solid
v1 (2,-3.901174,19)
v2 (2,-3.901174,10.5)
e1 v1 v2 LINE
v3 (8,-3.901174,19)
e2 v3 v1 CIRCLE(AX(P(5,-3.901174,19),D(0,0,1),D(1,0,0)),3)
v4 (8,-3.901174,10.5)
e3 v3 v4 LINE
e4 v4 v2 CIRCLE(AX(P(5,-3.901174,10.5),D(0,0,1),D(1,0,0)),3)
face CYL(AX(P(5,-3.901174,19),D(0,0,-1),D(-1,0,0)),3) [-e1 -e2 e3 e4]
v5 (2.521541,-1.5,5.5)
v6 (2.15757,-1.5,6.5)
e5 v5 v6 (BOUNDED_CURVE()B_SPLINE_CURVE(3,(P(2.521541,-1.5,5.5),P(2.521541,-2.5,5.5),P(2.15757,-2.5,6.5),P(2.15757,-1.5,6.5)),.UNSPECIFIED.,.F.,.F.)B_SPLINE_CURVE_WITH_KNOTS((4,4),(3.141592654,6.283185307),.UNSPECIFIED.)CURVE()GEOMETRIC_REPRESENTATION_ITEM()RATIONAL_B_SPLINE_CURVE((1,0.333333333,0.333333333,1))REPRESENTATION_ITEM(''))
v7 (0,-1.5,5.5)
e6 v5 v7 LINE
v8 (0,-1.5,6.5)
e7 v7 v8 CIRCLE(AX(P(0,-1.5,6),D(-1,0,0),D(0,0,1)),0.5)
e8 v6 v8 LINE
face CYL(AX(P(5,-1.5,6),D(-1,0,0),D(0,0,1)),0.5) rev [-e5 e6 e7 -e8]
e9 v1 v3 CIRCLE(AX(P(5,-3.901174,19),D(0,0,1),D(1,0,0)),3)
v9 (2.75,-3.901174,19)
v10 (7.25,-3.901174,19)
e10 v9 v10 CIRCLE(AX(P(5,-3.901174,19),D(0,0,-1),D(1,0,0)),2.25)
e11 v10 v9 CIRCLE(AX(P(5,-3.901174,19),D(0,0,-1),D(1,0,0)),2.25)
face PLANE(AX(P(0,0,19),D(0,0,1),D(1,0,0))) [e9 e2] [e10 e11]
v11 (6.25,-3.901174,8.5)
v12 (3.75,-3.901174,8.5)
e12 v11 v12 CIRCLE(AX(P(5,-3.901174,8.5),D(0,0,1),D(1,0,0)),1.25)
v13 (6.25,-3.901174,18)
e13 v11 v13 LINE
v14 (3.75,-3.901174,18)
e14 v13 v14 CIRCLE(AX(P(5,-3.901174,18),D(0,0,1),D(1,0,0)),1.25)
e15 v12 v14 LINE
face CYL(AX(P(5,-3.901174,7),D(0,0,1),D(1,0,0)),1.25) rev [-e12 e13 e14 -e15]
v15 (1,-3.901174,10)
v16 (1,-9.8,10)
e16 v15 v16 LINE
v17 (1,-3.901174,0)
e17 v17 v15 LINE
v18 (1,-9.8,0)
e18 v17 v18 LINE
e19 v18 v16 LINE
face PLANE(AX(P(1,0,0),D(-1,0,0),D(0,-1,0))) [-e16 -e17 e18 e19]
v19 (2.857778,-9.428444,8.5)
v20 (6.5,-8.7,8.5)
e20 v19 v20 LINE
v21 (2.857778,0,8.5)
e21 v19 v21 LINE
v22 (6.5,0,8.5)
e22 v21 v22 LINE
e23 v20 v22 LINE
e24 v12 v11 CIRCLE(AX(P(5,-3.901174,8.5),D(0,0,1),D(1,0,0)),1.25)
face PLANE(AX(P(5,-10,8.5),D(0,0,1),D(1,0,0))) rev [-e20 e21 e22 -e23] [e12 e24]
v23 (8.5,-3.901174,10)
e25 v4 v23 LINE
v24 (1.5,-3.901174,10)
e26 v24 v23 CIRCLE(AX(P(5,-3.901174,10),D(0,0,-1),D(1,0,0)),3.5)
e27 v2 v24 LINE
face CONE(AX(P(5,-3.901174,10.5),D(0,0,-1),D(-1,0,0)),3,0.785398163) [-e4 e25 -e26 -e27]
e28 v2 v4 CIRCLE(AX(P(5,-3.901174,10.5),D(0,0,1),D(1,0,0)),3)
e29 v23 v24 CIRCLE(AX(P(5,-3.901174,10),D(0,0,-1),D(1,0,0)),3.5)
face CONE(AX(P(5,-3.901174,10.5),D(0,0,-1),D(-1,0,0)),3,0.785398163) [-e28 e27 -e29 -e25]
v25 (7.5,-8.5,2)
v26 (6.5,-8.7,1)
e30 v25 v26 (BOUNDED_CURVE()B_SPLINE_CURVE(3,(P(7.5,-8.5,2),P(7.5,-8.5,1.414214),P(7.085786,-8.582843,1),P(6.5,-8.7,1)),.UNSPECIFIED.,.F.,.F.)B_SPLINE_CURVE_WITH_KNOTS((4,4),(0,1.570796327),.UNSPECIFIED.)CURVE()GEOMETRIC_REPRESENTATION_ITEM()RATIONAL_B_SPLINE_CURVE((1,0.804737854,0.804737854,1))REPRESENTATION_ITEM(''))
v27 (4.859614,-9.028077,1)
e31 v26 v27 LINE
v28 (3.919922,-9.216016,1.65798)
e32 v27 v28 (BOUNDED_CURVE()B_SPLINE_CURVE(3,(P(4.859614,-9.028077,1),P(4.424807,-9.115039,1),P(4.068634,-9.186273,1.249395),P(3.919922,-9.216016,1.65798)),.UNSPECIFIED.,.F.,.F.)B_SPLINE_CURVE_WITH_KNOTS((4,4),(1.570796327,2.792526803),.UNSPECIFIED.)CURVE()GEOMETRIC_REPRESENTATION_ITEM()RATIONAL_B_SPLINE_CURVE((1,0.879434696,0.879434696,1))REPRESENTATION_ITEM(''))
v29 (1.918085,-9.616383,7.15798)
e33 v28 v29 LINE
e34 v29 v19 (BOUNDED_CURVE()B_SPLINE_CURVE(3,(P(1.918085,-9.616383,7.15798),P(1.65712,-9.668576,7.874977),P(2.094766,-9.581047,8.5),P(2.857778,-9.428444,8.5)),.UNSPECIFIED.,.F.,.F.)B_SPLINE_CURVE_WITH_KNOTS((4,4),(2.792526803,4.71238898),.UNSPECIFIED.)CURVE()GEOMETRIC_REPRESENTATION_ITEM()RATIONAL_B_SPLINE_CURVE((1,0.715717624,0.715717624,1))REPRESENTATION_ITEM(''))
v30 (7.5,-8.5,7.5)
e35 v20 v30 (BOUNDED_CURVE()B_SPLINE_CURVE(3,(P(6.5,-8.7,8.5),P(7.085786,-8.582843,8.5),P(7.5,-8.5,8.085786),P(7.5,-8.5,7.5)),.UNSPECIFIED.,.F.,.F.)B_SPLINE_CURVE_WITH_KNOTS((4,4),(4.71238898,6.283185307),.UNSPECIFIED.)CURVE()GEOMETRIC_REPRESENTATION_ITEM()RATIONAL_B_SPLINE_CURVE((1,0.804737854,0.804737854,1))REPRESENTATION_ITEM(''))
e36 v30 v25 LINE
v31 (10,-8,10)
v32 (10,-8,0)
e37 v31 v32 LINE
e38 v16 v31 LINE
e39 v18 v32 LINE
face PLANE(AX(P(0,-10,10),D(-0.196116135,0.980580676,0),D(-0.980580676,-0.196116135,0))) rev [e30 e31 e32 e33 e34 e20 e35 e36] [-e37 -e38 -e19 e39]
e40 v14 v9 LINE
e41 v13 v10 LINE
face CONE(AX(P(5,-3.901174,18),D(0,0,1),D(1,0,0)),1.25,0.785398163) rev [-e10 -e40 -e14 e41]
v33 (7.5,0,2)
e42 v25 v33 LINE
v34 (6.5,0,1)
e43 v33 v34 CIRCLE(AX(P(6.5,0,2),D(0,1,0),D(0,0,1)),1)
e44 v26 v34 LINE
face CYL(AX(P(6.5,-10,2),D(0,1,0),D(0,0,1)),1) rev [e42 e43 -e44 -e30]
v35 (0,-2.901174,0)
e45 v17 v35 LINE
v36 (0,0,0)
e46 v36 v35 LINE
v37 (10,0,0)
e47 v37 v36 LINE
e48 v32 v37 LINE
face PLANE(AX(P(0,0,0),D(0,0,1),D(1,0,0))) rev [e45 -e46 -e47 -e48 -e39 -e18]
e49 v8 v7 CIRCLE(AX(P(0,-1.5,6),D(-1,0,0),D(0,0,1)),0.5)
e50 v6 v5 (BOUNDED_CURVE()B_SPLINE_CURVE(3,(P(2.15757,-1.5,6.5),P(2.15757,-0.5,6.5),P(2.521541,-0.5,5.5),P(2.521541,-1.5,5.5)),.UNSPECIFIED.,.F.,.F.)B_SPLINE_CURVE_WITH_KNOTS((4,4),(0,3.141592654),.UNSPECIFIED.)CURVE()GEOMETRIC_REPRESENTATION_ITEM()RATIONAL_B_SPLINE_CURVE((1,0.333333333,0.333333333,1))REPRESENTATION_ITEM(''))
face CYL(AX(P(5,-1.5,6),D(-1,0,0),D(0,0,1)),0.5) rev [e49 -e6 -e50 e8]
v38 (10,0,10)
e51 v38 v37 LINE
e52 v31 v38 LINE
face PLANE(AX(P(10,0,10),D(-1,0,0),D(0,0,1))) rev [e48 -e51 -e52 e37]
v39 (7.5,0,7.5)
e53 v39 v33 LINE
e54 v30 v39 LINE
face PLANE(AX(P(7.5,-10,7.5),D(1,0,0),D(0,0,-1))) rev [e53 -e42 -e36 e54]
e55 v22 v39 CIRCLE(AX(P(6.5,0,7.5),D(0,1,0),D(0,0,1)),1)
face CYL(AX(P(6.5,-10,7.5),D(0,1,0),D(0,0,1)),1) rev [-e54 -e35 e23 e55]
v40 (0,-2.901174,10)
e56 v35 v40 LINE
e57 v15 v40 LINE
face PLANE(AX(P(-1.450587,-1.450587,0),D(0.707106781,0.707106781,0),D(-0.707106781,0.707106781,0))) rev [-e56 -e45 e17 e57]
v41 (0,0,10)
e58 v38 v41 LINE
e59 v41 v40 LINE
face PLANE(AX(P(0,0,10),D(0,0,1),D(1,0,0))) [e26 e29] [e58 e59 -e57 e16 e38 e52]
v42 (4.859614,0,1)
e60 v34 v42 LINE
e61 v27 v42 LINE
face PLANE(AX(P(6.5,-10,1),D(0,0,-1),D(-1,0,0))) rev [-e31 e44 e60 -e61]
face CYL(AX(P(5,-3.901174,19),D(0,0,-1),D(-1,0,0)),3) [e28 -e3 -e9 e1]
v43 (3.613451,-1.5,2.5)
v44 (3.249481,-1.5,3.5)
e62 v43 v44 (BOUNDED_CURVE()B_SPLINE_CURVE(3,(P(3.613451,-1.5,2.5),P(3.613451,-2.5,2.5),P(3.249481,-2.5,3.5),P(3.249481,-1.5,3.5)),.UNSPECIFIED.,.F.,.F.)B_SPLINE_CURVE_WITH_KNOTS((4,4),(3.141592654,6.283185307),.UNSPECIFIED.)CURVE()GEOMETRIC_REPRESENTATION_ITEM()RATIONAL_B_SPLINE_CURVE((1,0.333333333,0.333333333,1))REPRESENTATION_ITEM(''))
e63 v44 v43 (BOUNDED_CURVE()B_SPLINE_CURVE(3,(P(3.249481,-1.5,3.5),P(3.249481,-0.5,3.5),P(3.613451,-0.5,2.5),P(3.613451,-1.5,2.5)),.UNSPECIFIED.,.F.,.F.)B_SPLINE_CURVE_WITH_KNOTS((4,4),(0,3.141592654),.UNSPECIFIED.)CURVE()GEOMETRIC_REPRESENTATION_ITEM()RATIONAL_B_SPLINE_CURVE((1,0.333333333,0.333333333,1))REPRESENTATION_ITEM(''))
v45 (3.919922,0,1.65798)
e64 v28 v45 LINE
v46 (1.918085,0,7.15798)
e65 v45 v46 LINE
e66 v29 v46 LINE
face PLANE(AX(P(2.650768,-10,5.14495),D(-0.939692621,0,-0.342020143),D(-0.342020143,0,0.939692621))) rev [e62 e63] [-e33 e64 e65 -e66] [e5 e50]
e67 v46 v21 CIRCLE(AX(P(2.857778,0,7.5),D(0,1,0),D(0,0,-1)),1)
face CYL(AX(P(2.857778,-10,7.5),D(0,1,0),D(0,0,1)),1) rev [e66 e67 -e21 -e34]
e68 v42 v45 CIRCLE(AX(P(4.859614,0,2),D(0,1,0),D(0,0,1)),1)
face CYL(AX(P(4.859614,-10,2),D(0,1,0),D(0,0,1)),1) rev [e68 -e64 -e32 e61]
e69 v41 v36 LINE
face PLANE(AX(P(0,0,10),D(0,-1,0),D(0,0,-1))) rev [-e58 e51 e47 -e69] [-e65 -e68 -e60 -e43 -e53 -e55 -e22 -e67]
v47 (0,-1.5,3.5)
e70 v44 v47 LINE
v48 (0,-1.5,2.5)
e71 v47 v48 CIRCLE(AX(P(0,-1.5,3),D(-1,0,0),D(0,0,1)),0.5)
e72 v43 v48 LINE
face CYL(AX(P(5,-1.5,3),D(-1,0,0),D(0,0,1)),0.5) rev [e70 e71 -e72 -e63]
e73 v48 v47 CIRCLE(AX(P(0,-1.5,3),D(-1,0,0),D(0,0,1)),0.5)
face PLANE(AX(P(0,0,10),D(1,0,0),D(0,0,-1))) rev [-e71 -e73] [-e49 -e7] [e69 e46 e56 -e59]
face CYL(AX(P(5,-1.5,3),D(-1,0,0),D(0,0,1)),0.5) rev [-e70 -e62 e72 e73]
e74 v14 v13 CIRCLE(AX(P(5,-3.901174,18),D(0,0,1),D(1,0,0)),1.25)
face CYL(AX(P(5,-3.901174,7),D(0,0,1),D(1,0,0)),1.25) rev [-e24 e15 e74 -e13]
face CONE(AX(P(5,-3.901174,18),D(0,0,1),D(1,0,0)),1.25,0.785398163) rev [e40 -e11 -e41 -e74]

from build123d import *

# Parameters (mm, degrees)
BASE_BLOCK_DEPTH        = 10
ROUND_SPIGOT_DEPTH      = 9
PROFILE_CUT_A_DEPTH     = 10
TRIANGULAR_POCKET_DEPTH = 10
PROFILE_CUT_B_SKETCH_R  = 0.5
PROFILE_CUT_B_DEPTH     = 5
SPIGOT_CHAMFER_0_5_SIZE = 0.5
SPIGOT_BORE_SKETCH_R    = 1.25
SPIGOT_BORE_DEPTH       = 12
BORE_CHAMFER_1_SIZE     = 1


with BuildPart() as part:
    # Base Block Sketch → Base Block (new body)
    with BuildSketch(Plane.XY):
        Polygon((0, 0), (10, 0), (10, -8), (0, -10), align=None)
    extrude(amount=BASE_BLOCK_DEPTH)

    # Spigot Sketch → Round Spigot (add)
    with BuildSketch(Plane.XY.offset(10)):
        with BuildLine():
            ThreePointArc((5, -0.901174016), (2, -3.901174016), (5, -6.901174016))
            Line((5, -6.901174016), (5, -3.901174016))
            Line((5, -3.901174016), (5, -0.901174016))
        make_face()
        with BuildLine():
            Line((5, -3.901174016), (5, -6.901174016))
            ThreePointArc((5, -6.901174016), (5.282604808, -6.887833442), (5.562696209, -6.847930365))
            Line((5.562696209, -6.847930365), (5, -3.901174016))
        make_face()
        with BuildLine():
            Line((5, -3.901174016), (5.562696209, -6.847930365))
            ThreePointArc((5.562696209, -6.847930365), (7.311718909, -5.813229373), (8, -3.901174016))
            ThreePointArc((8, -3.901174016), (7.121320344, -1.779853673), (5, -0.901174016))
            Line((5, -0.901174016), (5, -3.901174016))
        make_face()
    extrude(amount=ROUND_SPIGOT_DEPTH)

    # Profile Cut A Sketch → Profile Cut A (cut)
    with BuildSketch(Plane.XY.offset(10)):
        Polygon((1, -9.8), (1, -3.901174016), (0, -2.901174016), (0, -10), align=None)
    extrude(amount=-PROFILE_CUT_A_DEPTH, mode=Mode.SUBTRACT)

    # Triangular Pocket Sketch → Triangular Pocket (cut)
    with BuildSketch(Plane(origin=(0, 0, 0), x_dir=(1, 0, 0), z_dir=(0, 1, 0))):
        with BuildLine():
            Line((2.650768448, -5.144949642), (3.919921658, -1.657979857))
            ThreePointArc((3.919921658, -1.657979857), (4.286037842, -1.180847956), (4.859614278, -1))
            Line((4.859614278, -1), (6.5, -1))
            ThreePointArc((6.5, -1), (7.207106781, -1.292893219), (7.5, -2))
            Line((7.5, -2), (7.5, -7.5))
            ThreePointArc((7.5, -7.5), (7.207106781, -8.207106781), (6.5, -8.5))
            Line((6.5, -8.5), (5, -8.5))
            Line((5, -8.5), (2.85777799, -8.5))
            ThreePointArc((2.85777799, -8.5), (2.038625946, -8.073576436), (1.918085369, -7.157979857))
            Line((1.918085369, -7.157979857), (2.650768448, -5.144949642))
        make_face()
    extrude(amount=-TRIANGULAR_POCKET_DEPTH, mode=Mode.SUBTRACT)

    # Profile Cut B Sketch → Profile Cut B (cut)
    with BuildSketch(Plane.ZY):
        with Locations((3, -1.5)):
            Circle(PROFILE_CUT_B_SKETCH_R)
        with Locations((6, -1.5)):
            Circle(PROFILE_CUT_B_SKETCH_R)
    extrude(amount=-PROFILE_CUT_B_DEPTH, mode=Mode.SUBTRACT)

    # Spigot Chamfer 0.5
    spigot_chamfer_0_5_edges = [part.edges().sort_by_distance(p)[0] for p in [
        (4.437303791, -0.954417668, 10),
    ]]
    chamfer(spigot_chamfer_0_5_edges, length=SPIGOT_CHAMFER_0_5_SIZE)

    # Spigot Bore Sketch → Spigot Bore (cut)
    with BuildSketch(Plane.XY.offset(19)):
        with Locations((5, -3.901174016)):
            Circle(SPIGOT_BORE_SKETCH_R)
    extrude(amount=-SPIGOT_BORE_DEPTH, mode=Mode.SUBTRACT)

    # Bore Chamfer 1
    bore_chamfer_1_edges = [part.edges().sort_by_distance(p)[0] for p in [
        (3.75, -3.901174016, 19),
    ]]
    chamfer(bore_chamfer_1_edges, length=BORE_CHAMFER_1_SIZE)


solid = part.part
